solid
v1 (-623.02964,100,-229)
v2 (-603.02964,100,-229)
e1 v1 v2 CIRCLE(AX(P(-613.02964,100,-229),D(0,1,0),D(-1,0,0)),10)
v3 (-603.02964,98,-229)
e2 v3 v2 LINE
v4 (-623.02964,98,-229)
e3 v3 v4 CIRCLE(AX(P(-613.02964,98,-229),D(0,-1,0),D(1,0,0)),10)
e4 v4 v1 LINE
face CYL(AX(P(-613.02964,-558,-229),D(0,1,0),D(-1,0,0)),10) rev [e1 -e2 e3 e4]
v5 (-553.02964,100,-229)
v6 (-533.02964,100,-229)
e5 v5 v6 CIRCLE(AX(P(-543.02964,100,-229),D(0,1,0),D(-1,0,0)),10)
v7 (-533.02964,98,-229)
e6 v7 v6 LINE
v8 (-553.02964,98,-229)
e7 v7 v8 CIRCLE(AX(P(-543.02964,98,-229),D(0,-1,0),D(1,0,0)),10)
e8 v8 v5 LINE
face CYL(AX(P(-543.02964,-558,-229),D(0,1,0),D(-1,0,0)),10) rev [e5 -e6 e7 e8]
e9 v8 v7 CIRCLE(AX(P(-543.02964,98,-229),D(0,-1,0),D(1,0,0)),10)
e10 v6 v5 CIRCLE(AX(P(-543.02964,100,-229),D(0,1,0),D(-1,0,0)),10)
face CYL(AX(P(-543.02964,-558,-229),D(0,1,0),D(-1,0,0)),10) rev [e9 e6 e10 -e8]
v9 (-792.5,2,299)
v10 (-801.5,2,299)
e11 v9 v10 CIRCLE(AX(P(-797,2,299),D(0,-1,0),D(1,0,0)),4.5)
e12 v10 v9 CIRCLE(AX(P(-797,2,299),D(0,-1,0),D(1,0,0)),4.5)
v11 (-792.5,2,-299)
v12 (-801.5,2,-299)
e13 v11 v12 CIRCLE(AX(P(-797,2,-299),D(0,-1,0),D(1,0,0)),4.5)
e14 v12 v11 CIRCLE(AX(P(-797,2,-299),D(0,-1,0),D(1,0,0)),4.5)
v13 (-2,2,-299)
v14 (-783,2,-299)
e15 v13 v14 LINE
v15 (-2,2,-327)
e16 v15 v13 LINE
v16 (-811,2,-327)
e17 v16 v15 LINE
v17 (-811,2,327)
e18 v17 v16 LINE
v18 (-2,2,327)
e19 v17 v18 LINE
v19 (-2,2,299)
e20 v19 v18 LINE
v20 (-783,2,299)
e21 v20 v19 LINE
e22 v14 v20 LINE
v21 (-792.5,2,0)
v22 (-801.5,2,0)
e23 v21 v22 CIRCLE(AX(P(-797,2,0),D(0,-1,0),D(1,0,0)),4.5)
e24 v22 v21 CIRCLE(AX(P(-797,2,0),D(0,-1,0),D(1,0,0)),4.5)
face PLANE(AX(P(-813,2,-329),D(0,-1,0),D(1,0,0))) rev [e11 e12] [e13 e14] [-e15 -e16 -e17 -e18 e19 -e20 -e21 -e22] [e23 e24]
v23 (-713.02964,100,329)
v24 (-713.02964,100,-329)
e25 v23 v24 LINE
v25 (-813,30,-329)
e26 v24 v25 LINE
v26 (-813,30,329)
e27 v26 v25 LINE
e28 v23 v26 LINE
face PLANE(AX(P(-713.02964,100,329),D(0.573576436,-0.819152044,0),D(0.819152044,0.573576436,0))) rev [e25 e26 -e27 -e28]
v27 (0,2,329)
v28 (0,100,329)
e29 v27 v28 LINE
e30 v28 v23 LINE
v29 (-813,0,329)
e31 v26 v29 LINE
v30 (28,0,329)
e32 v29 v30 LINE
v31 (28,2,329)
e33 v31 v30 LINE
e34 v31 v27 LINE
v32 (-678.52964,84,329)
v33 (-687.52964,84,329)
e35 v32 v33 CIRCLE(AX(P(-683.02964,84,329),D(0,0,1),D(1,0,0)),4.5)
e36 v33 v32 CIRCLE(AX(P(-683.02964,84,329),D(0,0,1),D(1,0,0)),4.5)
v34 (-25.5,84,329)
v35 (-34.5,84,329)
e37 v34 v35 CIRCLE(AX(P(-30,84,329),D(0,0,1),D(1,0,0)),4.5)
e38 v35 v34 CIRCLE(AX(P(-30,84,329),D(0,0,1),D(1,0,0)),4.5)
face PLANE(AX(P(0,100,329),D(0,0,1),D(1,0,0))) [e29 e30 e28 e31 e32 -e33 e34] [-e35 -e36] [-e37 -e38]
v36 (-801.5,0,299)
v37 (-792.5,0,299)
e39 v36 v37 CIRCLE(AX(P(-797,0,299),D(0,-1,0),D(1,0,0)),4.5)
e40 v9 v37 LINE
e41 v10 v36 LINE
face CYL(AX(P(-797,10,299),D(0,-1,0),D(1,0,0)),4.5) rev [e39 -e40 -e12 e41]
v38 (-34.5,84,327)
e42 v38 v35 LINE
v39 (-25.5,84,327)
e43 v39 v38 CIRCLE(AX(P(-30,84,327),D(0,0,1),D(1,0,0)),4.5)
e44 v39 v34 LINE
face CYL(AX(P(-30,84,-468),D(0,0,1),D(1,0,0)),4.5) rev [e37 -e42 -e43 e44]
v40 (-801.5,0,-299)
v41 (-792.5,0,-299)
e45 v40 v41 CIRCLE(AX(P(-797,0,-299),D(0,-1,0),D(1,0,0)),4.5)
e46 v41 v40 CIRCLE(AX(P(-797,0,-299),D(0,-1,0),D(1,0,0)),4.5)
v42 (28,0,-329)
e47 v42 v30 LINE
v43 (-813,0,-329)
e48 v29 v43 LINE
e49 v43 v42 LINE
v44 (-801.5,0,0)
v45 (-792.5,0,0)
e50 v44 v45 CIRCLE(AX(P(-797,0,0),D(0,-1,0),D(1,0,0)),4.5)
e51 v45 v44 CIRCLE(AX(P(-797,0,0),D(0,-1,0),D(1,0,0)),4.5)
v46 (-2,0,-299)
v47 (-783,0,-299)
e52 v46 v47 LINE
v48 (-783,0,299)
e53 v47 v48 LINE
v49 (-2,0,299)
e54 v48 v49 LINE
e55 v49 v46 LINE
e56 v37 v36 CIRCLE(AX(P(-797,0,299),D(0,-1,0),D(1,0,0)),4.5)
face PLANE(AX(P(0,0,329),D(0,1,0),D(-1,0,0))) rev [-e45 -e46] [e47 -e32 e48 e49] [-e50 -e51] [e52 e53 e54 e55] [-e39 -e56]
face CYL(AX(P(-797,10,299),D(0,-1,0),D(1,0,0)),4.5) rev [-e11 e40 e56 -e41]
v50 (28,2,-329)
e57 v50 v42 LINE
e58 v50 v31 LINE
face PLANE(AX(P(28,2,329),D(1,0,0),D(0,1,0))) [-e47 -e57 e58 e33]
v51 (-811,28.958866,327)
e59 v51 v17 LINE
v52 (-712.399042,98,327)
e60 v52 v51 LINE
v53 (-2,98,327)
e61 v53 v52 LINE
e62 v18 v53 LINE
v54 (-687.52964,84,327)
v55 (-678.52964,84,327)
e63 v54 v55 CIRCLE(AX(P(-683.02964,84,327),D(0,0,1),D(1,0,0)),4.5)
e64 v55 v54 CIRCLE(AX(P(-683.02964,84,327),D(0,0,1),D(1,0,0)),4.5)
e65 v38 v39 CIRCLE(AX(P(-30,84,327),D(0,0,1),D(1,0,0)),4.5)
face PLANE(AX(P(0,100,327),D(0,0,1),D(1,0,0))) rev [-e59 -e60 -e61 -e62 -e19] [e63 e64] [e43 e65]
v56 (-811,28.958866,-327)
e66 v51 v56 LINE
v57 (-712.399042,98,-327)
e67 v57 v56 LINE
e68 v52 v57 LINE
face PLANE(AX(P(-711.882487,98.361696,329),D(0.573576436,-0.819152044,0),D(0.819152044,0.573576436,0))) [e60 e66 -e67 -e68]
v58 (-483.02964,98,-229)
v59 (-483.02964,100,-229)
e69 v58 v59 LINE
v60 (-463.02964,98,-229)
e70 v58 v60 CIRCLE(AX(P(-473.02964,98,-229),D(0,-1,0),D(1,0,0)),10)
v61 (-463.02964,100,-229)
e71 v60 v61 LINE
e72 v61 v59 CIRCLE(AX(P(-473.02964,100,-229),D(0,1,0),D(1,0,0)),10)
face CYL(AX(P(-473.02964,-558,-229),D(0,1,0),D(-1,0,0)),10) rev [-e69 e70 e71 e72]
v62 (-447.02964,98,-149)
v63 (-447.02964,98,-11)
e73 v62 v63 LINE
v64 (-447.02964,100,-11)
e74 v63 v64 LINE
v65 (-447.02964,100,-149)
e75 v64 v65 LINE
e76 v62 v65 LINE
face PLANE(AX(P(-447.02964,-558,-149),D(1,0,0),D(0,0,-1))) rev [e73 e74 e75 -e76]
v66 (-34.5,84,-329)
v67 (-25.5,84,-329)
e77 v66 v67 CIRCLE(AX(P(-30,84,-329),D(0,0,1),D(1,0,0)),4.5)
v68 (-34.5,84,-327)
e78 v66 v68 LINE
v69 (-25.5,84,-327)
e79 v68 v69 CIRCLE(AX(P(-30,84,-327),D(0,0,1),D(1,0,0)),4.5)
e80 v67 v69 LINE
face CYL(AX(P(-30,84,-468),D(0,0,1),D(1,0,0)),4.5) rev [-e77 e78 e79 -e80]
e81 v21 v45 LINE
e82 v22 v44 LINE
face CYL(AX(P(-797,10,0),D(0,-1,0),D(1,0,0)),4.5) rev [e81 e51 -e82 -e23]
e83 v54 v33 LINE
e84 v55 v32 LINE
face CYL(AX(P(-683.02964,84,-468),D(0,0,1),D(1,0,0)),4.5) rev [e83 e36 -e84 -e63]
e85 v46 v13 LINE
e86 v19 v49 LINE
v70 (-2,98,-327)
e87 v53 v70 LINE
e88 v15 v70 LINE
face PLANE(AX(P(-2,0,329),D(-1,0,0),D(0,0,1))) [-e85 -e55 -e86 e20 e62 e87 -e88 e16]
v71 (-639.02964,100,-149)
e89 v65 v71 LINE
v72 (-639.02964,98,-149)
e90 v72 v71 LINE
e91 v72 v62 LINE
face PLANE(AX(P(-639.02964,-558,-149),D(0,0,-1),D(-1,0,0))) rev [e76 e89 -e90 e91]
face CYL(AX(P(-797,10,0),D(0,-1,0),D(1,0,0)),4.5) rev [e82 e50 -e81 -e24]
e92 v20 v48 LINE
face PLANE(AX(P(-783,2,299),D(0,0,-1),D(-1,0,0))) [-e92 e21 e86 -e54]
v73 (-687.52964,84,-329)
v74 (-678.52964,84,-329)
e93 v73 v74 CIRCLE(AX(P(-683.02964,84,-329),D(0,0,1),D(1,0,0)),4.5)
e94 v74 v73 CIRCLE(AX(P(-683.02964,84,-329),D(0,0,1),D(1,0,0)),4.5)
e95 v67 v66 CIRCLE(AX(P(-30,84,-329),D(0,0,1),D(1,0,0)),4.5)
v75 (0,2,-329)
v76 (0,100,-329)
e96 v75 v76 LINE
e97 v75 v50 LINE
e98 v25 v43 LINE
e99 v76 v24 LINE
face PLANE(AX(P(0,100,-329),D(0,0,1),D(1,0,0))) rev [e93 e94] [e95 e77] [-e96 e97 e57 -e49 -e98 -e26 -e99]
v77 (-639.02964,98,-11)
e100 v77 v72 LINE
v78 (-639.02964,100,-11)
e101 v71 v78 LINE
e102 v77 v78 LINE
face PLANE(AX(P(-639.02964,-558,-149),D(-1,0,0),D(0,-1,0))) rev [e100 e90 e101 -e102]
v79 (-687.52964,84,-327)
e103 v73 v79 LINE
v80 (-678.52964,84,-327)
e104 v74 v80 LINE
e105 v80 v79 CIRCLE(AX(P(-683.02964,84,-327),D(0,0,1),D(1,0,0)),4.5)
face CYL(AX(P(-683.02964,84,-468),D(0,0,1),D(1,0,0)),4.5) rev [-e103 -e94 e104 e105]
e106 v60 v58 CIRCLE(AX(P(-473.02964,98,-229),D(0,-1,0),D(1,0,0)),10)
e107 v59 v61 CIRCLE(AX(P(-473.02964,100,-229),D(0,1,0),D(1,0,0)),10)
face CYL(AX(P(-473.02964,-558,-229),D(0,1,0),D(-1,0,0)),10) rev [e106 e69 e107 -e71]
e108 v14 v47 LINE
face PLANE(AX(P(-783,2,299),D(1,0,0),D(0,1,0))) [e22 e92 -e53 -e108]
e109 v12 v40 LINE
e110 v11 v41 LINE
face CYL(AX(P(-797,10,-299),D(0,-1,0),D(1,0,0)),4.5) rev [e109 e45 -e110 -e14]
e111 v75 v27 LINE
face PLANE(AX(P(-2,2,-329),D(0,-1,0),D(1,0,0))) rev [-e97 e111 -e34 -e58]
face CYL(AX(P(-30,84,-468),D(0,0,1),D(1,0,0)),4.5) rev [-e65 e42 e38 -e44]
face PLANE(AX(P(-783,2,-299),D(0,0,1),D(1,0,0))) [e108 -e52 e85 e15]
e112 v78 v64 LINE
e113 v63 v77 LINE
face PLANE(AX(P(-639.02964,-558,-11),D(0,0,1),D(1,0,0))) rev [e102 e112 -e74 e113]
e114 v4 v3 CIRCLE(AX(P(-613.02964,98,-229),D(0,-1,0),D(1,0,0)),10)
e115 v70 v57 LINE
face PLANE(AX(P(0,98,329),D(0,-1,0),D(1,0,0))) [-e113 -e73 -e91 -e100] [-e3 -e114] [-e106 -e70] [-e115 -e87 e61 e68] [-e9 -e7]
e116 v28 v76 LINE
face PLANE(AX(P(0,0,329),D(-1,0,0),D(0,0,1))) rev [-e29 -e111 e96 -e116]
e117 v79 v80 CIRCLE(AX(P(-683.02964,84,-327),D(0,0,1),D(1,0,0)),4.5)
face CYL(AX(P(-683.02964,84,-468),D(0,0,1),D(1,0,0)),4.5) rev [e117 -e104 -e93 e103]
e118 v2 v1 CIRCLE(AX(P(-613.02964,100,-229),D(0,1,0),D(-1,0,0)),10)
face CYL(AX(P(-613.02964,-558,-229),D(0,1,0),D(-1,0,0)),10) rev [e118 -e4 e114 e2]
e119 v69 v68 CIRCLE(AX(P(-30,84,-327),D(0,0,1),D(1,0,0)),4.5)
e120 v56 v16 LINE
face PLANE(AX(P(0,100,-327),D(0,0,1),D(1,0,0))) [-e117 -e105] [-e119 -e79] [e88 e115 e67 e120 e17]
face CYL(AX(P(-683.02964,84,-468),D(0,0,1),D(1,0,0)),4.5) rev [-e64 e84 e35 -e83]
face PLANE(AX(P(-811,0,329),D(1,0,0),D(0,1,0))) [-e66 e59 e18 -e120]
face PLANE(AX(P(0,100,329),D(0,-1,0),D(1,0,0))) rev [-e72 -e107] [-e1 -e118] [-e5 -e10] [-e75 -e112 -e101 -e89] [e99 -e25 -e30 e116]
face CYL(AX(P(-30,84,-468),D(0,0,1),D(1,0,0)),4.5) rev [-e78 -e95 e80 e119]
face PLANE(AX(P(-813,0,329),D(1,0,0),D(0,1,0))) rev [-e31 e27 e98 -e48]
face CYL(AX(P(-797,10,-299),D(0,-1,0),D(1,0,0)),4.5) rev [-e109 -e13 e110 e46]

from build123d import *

# Parameters (mm, degrees)
EXTRUDE_1_DEPTH     = 329
SHELL_1_T           = -2
SKETCH_2_R          = 10
SKETCH_2_W          = 192
SKETCH_2_H          = 138
CUT_EXTRUDE_1_DEPTH = 658
SKETCH_3_W          = 30
SKETCH_3_H          = 658
EXTRUDE_2_DEPTH     = 2
EXTRUDE_3_DEPTH     = 2
SKETCH_5_R          = 4.5
CUT_EXTRUDE_2_DEPTH = 797
SKETCH_6_R          = 4.5
CUT_EXTRUDE_3_DEPTH = 10


with BuildPart() as part:
    # 草图1 → 凸台-拉伸1 (new, symmetric)
    with BuildSketch(Plane.XY):
        Polygon((0, 0), (-813, 0), (-813, 30), (-713.029639528, 100), (0, 100), align=None)
    extrude(amount=EXTRUDE_1_DEPTH, both=True)

    # 抽壳1
    shell_1_openings = [part.faces().sort_by_distance(p)[0] for p in [
        (-406.5, 0, 0),
    ]]
    offset(amount=SHELL_1_T, openings=shell_1_openings, kind=Kind.INTERSECTION)

    # 草图2 → 切除-拉伸1 (cut)
    with BuildSketch(Plane(origin=(0, 100, 0), x_dir=(1, 0, 0), z_dir=(0, 1, 0))):
        with Locations(Location((-613.029639528, 229, 0), (0, 0, 180))):
            Circle(SKETCH_2_R)
        with Locations(Location((-543.029639528, 229, 0), (0, 0, 180))):
            Circle(SKETCH_2_R)
        with Locations((-473.029639528, 229)):
            Circle(SKETCH_2_R)
        with Locations((-543.029639528, 80)):
            Rectangle(SKETCH_2_W, SKETCH_2_H)
    extrude(amount=-CUT_EXTRUDE_1_DEPTH, mode=Mode.SUBTRACT)

    # 草图3 → 凸台-拉伸2 (add)
    with BuildSketch(Plane.XZ):
        with Locations((13, 0)):
            Rectangle(SKETCH_3_W, SKETCH_3_H)
    extrude(amount=-EXTRUDE_2_DEPTH)

    # 草图4 → 凸台-拉伸3 (add)
    with BuildSketch(Plane.XZ):
        Polygon((-783, 299), (-783, -299), (0, -299), (0, -329), (-813, -329), (-813, 329), (0, 329), (0, 299), align=None)
    extrude(amount=-EXTRUDE_3_DEPTH)

    # 草图5 → 切除-拉伸2 (cut)
    with BuildSketch(Plane.XY.offset(329)):
        with Locations((-683.029639528, 84)):
            Circle(SKETCH_5_R)
        with Locations((-30, 84)):
            Circle(SKETCH_5_R)
    extrude(amount=-CUT_EXTRUDE_2_DEPTH, mode=Mode.SUBTRACT)

    # 草图6 → 切除-拉伸3 (cut)
    with BuildSketch(Plane.XZ):
        with Locations((-797, 299)):
            Circle(SKETCH_6_R)
        with Locations((-797, -299)):
            Circle(SKETCH_6_R)
        with Locations((-797, 0)):
            Circle(SKETCH_6_R)
    extrude(amount=-CUT_EXTRUDE_3_DEPTH, mode=Mode.SUBTRACT)


solid = part.part
